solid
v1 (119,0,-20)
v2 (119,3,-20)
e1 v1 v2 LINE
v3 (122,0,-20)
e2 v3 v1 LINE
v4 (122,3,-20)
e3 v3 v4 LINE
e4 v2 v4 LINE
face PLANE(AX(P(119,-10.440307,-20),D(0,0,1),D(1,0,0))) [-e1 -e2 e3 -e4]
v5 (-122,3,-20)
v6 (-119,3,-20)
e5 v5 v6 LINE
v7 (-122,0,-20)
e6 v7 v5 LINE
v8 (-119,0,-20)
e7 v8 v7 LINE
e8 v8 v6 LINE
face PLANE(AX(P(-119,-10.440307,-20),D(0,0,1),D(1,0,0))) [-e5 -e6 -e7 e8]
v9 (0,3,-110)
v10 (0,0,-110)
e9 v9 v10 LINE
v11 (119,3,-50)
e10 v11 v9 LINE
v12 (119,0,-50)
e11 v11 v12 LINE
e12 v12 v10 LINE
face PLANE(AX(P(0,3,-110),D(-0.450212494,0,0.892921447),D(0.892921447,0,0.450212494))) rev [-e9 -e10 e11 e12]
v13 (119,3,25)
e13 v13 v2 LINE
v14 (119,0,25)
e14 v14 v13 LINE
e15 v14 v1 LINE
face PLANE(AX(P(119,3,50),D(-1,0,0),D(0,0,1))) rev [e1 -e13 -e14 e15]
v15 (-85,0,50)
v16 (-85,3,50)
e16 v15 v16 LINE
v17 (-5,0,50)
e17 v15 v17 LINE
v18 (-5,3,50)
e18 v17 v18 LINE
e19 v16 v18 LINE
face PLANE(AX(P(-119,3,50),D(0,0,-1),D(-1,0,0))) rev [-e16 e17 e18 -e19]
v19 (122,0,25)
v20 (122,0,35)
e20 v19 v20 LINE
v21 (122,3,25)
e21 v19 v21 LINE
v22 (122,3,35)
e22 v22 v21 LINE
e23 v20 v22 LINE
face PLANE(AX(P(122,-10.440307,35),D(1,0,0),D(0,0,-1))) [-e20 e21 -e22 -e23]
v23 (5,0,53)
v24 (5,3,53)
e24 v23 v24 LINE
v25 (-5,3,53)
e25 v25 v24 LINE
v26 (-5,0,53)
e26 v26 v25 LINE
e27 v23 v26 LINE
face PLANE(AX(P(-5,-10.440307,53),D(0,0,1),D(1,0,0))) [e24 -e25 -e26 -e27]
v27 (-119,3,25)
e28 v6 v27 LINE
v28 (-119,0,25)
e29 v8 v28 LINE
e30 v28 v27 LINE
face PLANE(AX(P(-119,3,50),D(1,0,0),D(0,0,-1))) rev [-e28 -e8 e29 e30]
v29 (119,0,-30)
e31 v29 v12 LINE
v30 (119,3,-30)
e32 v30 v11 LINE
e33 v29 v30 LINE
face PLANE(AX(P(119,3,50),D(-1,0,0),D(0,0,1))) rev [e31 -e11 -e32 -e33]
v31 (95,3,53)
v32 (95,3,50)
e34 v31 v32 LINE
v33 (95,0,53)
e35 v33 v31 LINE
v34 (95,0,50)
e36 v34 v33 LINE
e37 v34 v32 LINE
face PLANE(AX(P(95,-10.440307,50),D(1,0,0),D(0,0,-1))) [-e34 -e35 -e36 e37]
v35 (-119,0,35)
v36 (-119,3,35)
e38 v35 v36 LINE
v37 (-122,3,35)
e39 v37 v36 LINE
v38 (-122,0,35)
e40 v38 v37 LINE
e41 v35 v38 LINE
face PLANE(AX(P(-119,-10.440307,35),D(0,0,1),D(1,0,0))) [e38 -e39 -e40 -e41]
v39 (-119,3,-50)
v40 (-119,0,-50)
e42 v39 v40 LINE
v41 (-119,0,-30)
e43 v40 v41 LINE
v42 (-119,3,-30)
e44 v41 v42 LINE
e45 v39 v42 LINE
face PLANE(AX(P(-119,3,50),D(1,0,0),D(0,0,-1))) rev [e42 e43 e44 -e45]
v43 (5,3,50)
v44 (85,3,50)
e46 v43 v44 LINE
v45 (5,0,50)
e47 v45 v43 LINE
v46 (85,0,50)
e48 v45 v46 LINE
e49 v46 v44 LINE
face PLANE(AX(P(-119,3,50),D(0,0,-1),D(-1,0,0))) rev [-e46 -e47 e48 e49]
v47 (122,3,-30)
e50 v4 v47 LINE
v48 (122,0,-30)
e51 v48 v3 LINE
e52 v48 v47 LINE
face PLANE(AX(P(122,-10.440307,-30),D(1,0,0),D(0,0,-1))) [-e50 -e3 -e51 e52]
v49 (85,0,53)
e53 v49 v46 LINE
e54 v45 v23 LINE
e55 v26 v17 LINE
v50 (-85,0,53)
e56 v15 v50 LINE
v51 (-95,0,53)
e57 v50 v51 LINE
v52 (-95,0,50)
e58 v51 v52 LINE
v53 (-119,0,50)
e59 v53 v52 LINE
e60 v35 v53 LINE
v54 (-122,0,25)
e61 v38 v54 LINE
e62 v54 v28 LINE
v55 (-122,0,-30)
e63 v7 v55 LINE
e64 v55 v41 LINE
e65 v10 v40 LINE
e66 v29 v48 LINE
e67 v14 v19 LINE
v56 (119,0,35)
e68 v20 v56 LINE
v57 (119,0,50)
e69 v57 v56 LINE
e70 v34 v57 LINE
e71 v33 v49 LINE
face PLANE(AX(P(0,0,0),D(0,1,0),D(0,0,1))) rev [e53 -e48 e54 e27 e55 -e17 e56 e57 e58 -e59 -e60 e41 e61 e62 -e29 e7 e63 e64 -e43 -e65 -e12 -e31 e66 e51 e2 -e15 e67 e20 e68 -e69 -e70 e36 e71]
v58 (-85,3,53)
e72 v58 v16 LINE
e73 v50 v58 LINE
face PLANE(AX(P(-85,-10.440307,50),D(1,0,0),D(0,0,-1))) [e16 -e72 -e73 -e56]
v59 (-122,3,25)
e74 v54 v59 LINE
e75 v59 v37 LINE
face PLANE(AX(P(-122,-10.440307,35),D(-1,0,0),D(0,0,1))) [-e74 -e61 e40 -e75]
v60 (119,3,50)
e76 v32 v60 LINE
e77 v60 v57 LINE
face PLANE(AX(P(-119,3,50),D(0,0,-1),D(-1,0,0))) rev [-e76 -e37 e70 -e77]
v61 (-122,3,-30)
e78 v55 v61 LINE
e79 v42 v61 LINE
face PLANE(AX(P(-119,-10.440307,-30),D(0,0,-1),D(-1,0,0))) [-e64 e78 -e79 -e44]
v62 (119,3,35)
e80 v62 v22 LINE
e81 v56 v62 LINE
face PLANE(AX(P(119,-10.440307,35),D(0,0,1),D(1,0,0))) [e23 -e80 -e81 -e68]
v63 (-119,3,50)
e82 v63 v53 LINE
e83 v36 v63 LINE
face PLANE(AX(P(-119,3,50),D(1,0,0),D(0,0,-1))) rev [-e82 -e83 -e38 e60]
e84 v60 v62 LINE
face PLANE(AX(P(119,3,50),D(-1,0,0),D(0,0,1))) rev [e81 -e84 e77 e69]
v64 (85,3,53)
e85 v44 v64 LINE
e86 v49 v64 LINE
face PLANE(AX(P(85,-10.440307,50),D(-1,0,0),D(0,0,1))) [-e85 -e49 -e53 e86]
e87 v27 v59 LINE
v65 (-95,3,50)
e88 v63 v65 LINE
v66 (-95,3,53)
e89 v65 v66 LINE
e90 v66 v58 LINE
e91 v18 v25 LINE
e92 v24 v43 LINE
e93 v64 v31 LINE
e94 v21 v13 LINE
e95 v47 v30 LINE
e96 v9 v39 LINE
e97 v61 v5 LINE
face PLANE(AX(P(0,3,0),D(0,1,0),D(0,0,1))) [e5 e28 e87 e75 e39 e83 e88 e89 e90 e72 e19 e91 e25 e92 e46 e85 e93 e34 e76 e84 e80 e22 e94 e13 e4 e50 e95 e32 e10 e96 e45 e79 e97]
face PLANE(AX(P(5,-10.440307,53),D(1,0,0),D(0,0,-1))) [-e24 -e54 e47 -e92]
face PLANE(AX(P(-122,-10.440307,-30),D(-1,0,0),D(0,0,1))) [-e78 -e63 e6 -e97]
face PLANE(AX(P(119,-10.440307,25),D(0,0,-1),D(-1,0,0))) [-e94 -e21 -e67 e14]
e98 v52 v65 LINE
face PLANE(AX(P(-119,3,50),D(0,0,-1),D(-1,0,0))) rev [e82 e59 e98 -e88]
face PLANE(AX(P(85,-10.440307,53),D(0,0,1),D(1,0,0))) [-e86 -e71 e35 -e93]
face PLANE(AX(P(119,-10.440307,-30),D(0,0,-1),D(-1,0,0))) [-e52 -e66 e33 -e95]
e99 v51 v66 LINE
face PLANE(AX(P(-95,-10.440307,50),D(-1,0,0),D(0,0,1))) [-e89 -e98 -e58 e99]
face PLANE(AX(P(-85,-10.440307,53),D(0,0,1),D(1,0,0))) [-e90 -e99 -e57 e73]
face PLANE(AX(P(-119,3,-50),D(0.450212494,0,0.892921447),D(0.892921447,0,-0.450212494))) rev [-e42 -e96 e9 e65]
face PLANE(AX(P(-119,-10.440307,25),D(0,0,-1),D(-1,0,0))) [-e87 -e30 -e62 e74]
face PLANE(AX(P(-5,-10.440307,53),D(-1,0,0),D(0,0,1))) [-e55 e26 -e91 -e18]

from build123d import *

# Parameters (mm, degrees)
BOSS_EXTRUDE1_DEPTH = 3
SKETCH3_W           = 3
SKETCH3_H           = 10
SKETCH3_W_2         = 10
SKETCH3_H_2         = 3
BOSS_EXTRUDE2_DEPTH = 3


with BuildPart() as part:
    # Sketch1 → Boss-Extrude1 (new body)
    with BuildSketch(Plane(origin=(0, 0, 0), x_dir=(1, 0, 0), z_dir=(0, 1, 0))):
        Polygon((-119, 50), (0, 110), (119, 50), (119, -50), (-119, -50), align=None)
    extrude(amount=BOSS_EXTRUDE1_DEPTH)

    # Sketch3 → Boss-Extrude2 (add)
    with BuildSketch(Plane(origin=(0, 3, 0), x_dir=(1, 0, 0), z_dir=(0, 1, 0))):
        with Locations((120.5, 25)):
            Rectangle(SKETCH3_W, SKETCH3_H)
        with Locations((120.5, -30)):
            Rectangle(SKETCH3_W, SKETCH3_H)
        with Locations((-120.5, -30)):
            Rectangle(SKETCH3_W, SKETCH3_H)
        with Locations((-120.5, 25)):
            Rectangle(SKETCH3_W, SKETCH3_H)
        with Locations((-90, -51.5)):
            Rectangle(SKETCH3_W_2, SKETCH3_H_2)
        with Locations((90, -51.5)):
            Rectangle(SKETCH3_W_2, SKETCH3_H_2)
        with Locations((0, -51.5)):
            Rectangle(SKETCH3_W_2, SKETCH3_H_2)
    extrude(amount=-BOSS_EXTRUDE2_DEPTH)


solid = part.part
